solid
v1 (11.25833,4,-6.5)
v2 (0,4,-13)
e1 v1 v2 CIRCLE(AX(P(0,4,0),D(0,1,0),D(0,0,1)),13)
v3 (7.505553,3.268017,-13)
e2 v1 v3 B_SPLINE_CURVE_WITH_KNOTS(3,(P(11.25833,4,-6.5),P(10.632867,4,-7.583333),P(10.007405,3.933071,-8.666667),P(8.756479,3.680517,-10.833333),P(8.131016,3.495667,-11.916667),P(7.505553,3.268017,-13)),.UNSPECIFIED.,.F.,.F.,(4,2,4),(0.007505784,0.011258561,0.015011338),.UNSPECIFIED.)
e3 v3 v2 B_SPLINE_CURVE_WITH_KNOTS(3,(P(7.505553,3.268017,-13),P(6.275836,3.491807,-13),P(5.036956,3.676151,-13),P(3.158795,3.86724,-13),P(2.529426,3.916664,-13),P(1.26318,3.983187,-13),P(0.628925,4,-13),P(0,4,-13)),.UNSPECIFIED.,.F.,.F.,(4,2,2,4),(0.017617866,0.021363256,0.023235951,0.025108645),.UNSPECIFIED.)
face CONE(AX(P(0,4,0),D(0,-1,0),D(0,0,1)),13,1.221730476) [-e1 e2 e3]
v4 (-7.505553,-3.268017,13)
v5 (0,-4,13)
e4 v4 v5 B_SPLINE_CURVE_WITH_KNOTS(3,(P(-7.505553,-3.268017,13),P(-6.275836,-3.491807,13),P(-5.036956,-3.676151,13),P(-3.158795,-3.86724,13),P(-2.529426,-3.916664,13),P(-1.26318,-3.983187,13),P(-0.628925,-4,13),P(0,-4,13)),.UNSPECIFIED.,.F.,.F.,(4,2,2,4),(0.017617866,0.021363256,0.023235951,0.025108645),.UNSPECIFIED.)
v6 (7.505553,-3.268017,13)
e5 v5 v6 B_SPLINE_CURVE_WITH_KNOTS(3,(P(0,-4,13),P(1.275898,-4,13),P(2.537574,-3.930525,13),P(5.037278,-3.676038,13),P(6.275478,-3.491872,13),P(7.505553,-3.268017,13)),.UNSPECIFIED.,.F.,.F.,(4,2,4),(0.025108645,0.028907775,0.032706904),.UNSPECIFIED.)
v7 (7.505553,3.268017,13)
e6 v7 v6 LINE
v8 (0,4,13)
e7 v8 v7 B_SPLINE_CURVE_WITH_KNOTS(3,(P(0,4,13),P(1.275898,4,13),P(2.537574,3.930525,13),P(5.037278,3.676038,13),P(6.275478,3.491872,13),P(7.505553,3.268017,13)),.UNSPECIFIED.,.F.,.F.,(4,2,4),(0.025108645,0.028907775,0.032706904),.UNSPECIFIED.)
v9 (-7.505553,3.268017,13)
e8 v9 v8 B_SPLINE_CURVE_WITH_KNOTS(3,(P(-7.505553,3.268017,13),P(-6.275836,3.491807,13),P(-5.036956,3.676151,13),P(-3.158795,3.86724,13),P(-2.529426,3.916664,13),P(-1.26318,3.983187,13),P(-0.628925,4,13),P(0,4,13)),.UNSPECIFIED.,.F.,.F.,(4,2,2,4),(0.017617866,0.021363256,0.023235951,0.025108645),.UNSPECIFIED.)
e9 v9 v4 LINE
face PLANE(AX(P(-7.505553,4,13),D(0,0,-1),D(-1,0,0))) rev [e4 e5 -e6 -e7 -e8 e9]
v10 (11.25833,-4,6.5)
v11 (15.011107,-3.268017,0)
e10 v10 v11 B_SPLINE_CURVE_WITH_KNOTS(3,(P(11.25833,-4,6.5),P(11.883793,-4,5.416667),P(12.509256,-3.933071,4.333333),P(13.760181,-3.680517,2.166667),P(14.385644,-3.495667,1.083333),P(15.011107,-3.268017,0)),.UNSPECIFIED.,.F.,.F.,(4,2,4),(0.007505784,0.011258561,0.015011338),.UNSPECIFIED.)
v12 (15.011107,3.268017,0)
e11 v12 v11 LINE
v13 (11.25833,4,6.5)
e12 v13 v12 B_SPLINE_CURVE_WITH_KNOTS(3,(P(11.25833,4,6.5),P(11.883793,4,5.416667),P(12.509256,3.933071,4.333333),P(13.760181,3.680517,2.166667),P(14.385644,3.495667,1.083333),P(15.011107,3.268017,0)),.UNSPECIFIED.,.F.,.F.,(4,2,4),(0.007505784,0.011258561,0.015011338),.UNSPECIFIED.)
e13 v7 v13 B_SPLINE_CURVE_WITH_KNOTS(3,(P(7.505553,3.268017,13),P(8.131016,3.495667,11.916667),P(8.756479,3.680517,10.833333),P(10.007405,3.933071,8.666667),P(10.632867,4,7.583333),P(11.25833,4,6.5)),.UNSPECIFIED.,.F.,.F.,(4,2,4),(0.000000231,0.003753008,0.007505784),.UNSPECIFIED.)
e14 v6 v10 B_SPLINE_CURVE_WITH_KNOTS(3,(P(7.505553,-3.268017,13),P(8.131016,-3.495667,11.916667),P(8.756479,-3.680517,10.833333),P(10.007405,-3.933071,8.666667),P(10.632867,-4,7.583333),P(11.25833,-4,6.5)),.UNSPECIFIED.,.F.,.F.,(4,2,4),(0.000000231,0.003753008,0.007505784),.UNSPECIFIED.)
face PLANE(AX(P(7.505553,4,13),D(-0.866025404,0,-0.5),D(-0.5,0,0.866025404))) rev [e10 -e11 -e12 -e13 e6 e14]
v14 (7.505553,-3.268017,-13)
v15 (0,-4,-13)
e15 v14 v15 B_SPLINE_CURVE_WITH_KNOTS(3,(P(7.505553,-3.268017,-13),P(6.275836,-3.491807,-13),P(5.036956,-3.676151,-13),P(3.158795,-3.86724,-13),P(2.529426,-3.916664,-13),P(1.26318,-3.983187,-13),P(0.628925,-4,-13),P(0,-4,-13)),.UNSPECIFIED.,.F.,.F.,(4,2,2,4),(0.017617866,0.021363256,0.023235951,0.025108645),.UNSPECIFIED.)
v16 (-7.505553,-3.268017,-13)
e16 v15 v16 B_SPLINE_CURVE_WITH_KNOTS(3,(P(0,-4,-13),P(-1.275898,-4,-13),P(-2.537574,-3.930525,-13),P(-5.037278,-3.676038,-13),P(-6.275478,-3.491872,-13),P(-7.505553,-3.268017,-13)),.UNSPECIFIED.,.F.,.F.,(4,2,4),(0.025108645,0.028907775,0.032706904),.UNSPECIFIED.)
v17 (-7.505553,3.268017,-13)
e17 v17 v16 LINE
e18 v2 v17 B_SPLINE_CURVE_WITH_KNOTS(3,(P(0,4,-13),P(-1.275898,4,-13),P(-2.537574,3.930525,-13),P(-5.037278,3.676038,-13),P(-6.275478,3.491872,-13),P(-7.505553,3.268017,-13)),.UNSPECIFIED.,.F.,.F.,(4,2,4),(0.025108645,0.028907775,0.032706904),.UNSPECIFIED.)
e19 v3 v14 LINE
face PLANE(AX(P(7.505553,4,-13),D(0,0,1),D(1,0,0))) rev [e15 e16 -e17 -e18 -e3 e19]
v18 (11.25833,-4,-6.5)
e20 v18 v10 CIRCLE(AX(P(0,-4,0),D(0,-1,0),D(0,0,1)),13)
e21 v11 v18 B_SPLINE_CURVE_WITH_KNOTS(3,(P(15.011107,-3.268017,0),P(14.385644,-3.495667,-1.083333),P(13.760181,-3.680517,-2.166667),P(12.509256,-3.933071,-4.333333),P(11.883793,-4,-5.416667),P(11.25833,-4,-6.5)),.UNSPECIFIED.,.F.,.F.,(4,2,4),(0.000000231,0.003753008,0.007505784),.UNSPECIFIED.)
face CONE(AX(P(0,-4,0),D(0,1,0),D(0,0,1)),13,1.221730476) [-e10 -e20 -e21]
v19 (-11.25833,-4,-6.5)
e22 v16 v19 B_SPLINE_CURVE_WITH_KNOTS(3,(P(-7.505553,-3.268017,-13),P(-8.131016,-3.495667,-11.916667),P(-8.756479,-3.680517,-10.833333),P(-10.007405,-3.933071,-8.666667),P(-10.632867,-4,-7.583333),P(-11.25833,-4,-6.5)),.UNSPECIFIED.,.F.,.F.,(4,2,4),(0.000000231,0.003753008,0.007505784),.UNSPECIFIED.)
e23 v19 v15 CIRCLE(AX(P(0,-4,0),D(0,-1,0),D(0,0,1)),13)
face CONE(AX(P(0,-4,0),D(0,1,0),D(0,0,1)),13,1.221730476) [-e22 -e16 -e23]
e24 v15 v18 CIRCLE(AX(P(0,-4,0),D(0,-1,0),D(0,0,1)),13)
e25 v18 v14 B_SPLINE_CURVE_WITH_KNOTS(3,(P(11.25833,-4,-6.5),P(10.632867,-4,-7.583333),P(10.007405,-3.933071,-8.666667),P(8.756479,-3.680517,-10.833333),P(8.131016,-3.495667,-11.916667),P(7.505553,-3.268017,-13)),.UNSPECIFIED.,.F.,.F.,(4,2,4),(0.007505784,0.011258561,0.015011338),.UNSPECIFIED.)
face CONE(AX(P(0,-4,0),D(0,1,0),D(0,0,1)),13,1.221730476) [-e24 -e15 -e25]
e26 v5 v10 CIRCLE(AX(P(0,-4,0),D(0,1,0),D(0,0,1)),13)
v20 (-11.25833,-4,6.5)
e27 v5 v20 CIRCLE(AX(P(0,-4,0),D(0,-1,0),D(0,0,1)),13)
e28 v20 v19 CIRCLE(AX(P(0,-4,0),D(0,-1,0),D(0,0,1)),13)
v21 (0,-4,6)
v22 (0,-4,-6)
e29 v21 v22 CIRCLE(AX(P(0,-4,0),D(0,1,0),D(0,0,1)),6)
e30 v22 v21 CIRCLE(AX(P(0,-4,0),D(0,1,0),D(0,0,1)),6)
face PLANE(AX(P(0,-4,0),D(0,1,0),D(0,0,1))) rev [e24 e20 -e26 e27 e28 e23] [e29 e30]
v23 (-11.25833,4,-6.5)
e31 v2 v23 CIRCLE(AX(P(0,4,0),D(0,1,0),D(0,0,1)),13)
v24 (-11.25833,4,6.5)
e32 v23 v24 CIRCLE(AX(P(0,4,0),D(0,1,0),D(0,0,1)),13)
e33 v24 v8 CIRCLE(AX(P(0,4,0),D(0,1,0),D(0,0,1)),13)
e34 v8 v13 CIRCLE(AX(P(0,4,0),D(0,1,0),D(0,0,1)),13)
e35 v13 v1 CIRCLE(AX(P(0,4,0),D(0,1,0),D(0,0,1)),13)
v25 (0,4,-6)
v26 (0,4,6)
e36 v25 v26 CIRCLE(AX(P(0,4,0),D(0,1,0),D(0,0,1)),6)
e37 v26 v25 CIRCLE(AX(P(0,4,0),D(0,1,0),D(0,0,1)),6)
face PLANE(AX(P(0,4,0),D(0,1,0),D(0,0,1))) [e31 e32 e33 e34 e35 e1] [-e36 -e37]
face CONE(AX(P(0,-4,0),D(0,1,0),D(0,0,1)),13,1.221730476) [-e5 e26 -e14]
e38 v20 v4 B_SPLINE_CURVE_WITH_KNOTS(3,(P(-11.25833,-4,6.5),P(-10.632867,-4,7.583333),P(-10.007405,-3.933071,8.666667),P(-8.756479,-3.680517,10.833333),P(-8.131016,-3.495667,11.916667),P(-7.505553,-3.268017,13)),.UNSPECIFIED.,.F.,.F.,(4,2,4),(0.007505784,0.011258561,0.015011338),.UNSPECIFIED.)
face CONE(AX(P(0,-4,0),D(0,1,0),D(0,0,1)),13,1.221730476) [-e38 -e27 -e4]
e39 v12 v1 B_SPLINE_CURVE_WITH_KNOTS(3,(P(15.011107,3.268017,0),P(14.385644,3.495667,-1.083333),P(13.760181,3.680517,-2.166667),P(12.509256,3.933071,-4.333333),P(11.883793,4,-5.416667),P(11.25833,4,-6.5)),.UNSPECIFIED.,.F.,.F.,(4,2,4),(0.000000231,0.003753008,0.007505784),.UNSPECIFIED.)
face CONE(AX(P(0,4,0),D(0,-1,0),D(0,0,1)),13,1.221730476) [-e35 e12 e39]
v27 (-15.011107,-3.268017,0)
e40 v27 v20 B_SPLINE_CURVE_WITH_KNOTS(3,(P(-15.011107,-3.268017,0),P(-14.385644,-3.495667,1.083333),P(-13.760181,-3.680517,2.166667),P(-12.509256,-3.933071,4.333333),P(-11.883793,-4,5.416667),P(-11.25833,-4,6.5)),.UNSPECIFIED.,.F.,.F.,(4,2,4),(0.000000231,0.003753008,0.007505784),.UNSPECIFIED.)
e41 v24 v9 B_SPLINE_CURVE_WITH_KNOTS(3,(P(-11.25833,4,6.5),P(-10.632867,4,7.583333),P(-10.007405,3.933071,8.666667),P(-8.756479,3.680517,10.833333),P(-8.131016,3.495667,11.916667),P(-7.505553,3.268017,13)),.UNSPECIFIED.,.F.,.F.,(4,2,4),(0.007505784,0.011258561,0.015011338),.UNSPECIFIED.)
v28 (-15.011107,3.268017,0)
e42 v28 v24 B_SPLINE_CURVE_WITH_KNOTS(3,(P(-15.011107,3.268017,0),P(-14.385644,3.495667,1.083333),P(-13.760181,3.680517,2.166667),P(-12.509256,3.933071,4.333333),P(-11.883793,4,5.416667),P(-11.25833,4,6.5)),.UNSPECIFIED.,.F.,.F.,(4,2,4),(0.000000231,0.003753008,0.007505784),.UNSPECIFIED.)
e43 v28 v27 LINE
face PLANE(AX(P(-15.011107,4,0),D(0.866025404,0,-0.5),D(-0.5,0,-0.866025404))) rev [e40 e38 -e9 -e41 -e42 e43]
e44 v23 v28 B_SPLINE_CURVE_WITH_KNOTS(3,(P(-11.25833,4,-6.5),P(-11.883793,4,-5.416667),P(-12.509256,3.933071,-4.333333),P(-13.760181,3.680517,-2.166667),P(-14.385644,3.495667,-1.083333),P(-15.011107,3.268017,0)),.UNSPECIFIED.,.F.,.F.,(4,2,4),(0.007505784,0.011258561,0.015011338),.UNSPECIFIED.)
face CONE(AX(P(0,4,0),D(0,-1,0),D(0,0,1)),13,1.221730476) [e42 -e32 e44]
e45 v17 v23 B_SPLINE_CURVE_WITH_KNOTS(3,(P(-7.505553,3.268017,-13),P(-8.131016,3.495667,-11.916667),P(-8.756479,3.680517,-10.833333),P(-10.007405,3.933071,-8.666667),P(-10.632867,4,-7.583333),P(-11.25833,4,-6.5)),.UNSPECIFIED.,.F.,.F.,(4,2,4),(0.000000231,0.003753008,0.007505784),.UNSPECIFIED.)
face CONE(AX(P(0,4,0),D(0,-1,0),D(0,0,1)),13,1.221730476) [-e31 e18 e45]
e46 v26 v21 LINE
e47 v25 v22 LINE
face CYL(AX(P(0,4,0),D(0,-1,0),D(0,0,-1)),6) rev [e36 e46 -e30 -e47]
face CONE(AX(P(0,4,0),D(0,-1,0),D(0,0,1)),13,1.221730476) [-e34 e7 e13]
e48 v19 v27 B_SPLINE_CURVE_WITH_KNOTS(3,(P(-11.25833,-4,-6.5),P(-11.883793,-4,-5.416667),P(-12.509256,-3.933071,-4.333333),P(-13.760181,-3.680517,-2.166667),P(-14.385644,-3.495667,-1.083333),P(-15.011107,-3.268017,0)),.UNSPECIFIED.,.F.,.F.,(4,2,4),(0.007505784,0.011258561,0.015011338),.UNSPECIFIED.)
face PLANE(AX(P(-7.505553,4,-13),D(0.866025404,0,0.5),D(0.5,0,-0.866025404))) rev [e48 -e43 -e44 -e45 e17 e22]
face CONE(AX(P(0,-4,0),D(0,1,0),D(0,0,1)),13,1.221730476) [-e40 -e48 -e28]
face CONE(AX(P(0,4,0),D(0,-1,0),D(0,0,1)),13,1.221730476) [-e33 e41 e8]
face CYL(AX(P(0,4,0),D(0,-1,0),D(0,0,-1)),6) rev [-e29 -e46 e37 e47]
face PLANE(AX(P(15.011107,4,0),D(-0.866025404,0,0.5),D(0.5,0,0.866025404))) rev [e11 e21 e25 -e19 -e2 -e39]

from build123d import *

# Parameters (mm, degrees)
HEX_PROFILE_SKETCH_R                  = 6
HEX_NUT_BODY_DEPTH                    = 4
CHAMFER_CIRCLE_SKETCH_OUTSIDE_W       = 163.26
CHAMFER_CIRCLE_SKETCH_OUTSIDE_H       = 159.238
CHAMFER_CIRCLE_SKETCH_OUTSIDE_R       = 13
TOP_CHAMFER_CUT_70DEG_DEPTH           = 22.408720964
TOP_CHAMFER_CUT_70DEG_DRAFT           = -70
BOTTOM_CHAMFER_MIRROR_COPY_1_SKETCH_W = 163.26
BOTTOM_CHAMFER_MIRROR_COPY_1_SKETCH_H = 159.238
BOTTOM_CHAMFER_MIRROR_COPY_1_SKETCH_R = 13
BOTTOM_CHAMFER_MIRROR_COPY_1_DEPTH    = 22.408720964
BOTTOM_CHAMFER_MIRROR_COPY_1_DRAFT    = -70


with BuildPart() as part:
    # Hex Profile Sketch → Hex Nut Body (new, symmetric)
    with BuildSketch(Plane(origin=(0, 0, 0), x_dir=(1, 0, 0), z_dir=(0, 1, 0))):
        Polygon((15.011106999, 0), (7.505553499, 13), (-7.505553499, 13), (-15.011106999, 0), (-7.505553499, -13), (7.505553499, -13), align=None)
        with Locations(Location((0, 0, 0), (0, 0, 270))):
            Circle(HEX_PROFILE_SKETCH_R, mode=Mode.SUBTRACT)
    extrude(amount=HEX_NUT_BODY_DEPTH, both=True)


with BuildPart() as top_chamfer_cut_70deg_tool:
    # Chamfer Circle Sketch outside → Top Chamfer Cut 70deg (with draft: the straight prism first)
    with BuildSketch(Plane(origin=(0, 4, 0), x_dir=(1, 0, 0), z_dir=(0, 1, 0))):
        Rectangle(CHAMFER_CIRCLE_SKETCH_OUTSIDE_W, CHAMFER_CIRCLE_SKETCH_OUTSIDE_H)
        Circle(CHAMFER_CIRCLE_SKETCH_OUTSIDE_R, mode=Mode.SUBTRACT)
    extrude(amount=-TOP_CHAMFER_CUT_70DEG_DEPTH)
    # Top Chamfer Cut 70deg: the draft: its side faces are tilted about the plane it starts from
    top_chamfer_cut_70deg_sides = [top_chamfer_cut_70deg_tool.faces().sort_by_distance(p)[0] for p in [
        (0, -7.204360482, 79.619),
        (81.63, -7.204360482, 0),
        (0, -7.204360482, -79.619),
        (-81.63, -7.204360482, 0),
        (-13, -7.204360482, 0),
    ]]
    draft(top_chamfer_cut_70deg_sides, Plane(origin=(0, 4, 0), x_dir=(1, 0, 0), z_dir=(0, 1, 0)), TOP_CHAMFER_CUT_70DEG_DRAFT)


with BuildPart() as part_1:
    add(part.part)

    # Top Chamfer Cut 70deg: cut by top_chamfer_cut_70deg_tool
    add(top_chamfer_cut_70deg_tool.part, mode=Mode.SUBTRACT)


with BuildPart() as bottom_chamfer_mirror_copy_1_tool:
    # Bottom Chamfer Mirror copy 1 sketch → Bottom Chamfer Mirror copy 1 (with draft: the straight prism first)
    with BuildSketch(Plane.XZ.offset(4)):
        Rectangle(BOTTOM_CHAMFER_MIRROR_COPY_1_SKETCH_W, BOTTOM_CHAMFER_MIRROR_COPY_1_SKETCH_H)
        Circle(BOTTOM_CHAMFER_MIRROR_COPY_1_SKETCH_R, mode=Mode.SUBTRACT)
    extrude(amount=-BOTTOM_CHAMFER_MIRROR_COPY_1_DEPTH)
    # Bottom Chamfer Mirror copy 1: the draft: its side faces are tilted about the plane it starts from
    bottom_chamfer_mirror_copy_1_sides = [bottom_chamfer_mirror_copy_1_tool.faces().sort_by_distance(p)[0] for p in [
        (0, 7.204360482, 79.619),
        (81.63, 7.204360482, 0),
        (0, 7.204360482, -79.619),
        (-81.63, 7.204360482, 0),
        (-13, 7.204360482, 0),
    ]]
    draft(bottom_chamfer_mirror_copy_1_sides, Plane.XZ.offset(4), BOTTOM_CHAMFER_MIRROR_COPY_1_DRAFT)


with BuildPart() as part_2:
    add(part_1.part)

    # Bottom Chamfer Mirror copy 1: cut by bottom_chamfer_mirror_copy_1_tool
    add(bottom_chamfer_mirror_copy_1_tool.part, mode=Mode.SUBTRACT)


solid = part_2.part
